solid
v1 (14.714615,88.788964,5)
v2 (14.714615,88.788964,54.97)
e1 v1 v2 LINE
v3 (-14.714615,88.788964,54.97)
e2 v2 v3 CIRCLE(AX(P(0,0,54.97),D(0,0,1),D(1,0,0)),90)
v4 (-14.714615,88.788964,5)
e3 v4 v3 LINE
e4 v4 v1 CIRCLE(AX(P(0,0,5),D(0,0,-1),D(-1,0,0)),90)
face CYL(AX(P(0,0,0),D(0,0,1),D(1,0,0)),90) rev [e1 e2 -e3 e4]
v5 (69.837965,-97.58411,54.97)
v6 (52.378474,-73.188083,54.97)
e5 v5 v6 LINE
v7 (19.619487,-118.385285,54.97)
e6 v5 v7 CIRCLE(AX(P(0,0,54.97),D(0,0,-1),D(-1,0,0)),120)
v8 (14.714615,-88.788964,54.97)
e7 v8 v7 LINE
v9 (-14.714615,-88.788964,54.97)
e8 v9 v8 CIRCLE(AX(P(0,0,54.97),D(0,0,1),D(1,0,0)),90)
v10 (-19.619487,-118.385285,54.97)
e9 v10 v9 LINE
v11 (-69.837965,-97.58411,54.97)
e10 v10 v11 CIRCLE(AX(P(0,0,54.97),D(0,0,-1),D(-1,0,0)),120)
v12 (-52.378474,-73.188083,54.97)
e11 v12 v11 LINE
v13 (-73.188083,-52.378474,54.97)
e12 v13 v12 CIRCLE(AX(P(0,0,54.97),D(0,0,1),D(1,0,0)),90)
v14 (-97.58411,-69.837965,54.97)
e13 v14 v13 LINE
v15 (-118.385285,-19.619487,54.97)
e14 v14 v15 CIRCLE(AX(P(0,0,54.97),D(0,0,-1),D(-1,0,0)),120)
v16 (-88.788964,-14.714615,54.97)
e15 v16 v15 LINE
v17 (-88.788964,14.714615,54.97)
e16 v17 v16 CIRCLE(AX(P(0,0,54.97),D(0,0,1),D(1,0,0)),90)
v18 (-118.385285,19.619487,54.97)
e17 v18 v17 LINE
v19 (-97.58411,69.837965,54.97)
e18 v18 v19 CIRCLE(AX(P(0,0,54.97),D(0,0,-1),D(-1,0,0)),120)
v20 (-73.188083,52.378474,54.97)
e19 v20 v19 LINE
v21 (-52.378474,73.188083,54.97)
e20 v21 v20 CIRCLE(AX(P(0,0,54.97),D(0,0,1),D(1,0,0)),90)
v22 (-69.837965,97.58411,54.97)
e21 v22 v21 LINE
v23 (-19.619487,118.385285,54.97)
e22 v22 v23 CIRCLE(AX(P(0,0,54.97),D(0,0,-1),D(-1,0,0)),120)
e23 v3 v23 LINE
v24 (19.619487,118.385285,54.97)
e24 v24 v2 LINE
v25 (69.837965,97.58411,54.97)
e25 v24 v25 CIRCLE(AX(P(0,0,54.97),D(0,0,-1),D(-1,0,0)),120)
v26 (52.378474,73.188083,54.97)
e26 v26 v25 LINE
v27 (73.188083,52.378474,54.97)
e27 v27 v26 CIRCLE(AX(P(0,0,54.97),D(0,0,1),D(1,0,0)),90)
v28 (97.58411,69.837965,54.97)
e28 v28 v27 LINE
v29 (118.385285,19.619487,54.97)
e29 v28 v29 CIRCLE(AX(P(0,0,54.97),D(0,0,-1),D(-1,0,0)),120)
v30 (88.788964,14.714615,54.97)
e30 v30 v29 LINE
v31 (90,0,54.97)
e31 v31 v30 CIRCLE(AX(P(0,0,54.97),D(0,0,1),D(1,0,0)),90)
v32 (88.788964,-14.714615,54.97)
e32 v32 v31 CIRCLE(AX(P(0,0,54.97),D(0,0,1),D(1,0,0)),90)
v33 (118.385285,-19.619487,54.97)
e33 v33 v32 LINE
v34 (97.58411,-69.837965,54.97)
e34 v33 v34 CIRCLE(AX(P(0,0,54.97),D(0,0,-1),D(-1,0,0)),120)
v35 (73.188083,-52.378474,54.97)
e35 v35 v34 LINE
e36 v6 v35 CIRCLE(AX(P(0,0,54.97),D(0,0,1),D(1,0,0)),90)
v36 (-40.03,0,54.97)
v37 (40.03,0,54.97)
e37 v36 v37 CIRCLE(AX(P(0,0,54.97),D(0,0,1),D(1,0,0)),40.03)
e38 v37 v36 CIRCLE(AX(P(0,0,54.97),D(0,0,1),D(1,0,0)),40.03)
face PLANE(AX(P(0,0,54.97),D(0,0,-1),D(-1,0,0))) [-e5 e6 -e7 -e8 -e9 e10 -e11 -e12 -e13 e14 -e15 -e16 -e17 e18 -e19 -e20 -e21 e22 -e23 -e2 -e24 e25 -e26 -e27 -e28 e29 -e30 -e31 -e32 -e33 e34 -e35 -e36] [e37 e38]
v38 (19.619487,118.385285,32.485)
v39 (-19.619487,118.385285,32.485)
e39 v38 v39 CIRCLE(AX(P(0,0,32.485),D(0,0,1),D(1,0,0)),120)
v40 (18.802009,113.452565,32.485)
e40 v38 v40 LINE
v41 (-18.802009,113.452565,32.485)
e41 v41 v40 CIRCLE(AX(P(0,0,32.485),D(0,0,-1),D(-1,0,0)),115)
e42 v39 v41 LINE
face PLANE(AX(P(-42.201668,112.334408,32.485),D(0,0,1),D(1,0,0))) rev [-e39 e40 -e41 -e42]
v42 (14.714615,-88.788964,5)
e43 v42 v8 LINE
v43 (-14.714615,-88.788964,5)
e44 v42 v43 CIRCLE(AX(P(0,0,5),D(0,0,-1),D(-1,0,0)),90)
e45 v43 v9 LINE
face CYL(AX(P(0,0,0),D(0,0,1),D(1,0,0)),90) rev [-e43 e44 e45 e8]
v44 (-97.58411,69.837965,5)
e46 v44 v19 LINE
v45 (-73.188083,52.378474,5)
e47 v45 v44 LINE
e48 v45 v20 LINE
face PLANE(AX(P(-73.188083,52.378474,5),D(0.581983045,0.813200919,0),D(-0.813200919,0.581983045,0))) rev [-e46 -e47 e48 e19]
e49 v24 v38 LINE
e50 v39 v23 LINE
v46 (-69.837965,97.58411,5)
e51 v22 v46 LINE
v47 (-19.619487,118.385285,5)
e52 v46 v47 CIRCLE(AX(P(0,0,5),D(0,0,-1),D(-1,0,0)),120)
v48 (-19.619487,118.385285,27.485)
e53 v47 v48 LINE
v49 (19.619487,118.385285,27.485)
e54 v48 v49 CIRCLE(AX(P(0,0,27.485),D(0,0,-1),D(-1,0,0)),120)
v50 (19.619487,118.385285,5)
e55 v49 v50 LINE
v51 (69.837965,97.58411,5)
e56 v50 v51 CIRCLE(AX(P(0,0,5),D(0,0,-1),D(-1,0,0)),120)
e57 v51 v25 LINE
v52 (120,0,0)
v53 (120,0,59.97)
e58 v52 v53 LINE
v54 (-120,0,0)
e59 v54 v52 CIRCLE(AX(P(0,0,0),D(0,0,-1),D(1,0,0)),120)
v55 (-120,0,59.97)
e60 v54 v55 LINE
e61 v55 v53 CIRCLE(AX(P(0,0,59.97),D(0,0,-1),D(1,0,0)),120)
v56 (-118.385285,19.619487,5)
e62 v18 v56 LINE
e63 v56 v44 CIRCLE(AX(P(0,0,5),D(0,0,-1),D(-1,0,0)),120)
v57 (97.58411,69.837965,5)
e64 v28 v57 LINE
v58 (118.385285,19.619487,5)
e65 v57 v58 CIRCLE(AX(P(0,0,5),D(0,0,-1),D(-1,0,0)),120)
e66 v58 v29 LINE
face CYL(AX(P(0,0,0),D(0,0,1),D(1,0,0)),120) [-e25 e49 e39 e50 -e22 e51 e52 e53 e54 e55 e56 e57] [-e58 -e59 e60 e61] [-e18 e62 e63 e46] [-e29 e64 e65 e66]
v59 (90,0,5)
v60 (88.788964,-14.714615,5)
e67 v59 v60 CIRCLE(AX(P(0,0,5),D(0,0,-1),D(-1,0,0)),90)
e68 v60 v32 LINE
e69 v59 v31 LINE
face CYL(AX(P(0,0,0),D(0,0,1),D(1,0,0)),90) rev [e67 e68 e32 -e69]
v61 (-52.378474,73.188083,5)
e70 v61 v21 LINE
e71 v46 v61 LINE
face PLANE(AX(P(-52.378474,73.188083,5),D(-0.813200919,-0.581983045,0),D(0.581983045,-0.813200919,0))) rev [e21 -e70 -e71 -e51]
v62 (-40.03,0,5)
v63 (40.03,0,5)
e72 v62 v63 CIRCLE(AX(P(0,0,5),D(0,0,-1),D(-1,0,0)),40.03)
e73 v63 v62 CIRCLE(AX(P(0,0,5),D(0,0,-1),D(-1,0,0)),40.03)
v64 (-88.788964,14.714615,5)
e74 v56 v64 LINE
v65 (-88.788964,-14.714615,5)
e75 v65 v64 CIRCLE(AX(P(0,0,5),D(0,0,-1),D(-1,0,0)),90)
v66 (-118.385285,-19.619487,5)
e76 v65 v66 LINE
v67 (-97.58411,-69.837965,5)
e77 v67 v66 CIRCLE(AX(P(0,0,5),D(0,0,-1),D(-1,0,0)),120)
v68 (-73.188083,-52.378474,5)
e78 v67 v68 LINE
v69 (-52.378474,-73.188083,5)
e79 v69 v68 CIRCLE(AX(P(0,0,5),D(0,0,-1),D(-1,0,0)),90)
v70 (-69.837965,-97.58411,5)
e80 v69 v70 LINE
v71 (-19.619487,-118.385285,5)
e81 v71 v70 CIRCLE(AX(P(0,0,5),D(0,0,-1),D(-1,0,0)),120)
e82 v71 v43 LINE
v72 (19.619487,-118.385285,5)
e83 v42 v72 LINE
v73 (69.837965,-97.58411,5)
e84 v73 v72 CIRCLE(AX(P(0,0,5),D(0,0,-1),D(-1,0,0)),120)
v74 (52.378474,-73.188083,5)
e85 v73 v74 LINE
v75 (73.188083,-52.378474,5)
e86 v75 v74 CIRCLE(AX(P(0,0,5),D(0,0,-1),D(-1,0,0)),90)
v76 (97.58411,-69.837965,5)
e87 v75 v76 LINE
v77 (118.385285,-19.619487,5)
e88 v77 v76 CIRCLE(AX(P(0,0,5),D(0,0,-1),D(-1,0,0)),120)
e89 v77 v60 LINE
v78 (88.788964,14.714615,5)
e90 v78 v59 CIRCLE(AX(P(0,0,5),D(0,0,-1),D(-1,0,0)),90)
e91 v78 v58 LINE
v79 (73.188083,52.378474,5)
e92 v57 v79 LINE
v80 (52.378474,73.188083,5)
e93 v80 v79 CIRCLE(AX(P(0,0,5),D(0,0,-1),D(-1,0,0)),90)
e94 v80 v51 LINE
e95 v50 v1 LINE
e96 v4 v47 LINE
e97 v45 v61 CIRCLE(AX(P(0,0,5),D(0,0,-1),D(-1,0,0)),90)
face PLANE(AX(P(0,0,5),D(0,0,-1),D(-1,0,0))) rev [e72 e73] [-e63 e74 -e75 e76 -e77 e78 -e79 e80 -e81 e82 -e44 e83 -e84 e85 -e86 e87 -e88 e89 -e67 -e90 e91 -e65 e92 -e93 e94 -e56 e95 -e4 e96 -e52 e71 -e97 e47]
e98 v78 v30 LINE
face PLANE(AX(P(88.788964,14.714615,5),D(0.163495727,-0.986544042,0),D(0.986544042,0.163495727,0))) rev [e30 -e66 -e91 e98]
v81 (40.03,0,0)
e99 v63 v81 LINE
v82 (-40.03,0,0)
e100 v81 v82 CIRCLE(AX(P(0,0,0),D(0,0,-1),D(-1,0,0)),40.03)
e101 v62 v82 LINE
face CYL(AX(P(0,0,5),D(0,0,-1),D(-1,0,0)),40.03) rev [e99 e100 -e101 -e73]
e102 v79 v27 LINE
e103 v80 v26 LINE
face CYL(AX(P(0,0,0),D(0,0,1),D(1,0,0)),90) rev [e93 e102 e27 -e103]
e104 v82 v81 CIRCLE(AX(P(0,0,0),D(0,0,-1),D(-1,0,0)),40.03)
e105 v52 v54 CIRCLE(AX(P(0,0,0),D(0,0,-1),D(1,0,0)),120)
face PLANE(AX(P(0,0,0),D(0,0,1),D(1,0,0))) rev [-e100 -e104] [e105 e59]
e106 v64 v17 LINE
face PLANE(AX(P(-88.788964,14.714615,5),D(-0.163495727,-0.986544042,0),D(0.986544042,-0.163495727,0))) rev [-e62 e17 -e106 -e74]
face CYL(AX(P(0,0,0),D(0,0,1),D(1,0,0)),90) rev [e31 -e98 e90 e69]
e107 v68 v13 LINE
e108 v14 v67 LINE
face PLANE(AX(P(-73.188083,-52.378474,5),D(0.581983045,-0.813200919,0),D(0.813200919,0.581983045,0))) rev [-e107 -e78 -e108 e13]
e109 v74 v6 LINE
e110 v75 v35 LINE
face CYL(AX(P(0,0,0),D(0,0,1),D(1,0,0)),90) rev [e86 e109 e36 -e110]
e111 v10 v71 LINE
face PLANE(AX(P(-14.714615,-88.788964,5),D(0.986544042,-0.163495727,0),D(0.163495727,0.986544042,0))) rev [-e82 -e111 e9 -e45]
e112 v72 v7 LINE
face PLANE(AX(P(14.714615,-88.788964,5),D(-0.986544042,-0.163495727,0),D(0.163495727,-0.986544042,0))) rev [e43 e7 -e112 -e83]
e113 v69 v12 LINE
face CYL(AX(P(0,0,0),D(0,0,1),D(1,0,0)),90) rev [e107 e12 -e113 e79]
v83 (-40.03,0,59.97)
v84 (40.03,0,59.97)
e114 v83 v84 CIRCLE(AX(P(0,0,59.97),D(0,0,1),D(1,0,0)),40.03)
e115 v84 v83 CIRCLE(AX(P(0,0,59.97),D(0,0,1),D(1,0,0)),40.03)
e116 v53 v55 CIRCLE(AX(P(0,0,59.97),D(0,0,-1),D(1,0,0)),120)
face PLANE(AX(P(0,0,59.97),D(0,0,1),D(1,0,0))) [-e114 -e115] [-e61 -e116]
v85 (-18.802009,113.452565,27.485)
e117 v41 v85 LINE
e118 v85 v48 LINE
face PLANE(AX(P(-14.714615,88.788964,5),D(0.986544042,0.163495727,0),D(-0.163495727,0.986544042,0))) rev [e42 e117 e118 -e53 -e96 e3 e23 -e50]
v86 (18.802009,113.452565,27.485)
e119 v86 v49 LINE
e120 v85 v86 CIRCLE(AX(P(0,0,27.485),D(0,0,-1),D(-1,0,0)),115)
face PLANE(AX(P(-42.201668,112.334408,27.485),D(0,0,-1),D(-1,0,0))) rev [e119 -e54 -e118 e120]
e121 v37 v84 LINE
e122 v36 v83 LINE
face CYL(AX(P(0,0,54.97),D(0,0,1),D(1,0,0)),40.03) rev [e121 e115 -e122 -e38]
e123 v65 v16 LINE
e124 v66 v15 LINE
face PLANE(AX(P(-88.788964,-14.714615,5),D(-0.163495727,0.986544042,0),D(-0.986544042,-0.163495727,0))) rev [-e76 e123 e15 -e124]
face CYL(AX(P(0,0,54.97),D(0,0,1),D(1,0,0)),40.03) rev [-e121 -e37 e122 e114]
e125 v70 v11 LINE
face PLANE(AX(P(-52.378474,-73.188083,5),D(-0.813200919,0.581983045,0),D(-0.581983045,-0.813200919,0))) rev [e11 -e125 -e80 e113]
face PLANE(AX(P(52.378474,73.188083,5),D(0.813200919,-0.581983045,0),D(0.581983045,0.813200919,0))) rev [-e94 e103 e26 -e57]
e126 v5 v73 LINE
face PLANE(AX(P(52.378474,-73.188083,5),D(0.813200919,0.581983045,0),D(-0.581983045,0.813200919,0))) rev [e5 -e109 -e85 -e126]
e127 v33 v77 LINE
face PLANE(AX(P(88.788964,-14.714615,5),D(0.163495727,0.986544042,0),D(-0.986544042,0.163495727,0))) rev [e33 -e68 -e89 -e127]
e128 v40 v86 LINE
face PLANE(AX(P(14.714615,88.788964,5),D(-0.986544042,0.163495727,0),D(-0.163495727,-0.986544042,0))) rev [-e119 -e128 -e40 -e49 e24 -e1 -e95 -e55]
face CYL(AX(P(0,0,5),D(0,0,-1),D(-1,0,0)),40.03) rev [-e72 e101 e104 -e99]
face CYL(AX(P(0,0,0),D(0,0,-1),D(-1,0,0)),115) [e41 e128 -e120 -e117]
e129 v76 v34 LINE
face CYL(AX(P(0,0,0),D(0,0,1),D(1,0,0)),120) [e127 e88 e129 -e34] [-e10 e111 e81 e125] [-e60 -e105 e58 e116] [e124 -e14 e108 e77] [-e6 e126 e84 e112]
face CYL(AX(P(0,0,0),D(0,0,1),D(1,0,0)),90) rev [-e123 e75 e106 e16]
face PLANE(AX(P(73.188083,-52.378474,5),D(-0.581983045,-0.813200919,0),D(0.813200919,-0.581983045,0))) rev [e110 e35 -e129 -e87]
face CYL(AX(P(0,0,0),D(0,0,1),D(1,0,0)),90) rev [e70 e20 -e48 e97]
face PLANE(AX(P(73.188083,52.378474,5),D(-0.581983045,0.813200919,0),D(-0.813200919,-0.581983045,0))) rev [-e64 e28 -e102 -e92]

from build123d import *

# Parameters (mm, degrees)
SKETCH1_R           = 150
SKETCH1_R_2         = 120
BOSS_EXTRUDE1_DEPTH = 59.97
BOSS_EXTRUDE2_START = -59.97
SKETCH2_R           = 120
SKETCH2_R_2         = 90
BOSS_EXTRUDE2_DEPTH = 59.97
CUT_EXTRUDE1_START  = -59.97
CUT_EXTRUDE1_DEPTH  = 59.97
CIRPATTERN1_COUNT   = 8
CUT_EXTRUDE2_START  = -49.97
CUT_EXTRUDE2_DEPTH  = 49.97
CIRPATTERN2_COUNT   = 8
BOSS_EXTRUDE3_START = -5
SKETCH6_R           = 90
SKETCH6_R_2         = 40.03
BOSS_EXTRUDE3_DEPTH = 5
SKETCH7_R           = 90
SKETCH7_R_2         = 40.03
BOSS_EXTRUDE4_DEPTH = 5
SKETCH8_R           = 150
SKETCH8_R_2         = 120
CUT_EXTRUDE3_DEPTH  = 80
SKETCH10_W          = 5
SKETCH10_H          = 5
CUT_REVOLVE1_ANGLE  = 30


with BuildPart() as part:
    # Sketch1 → Boss-Extrude1 (new body)
    with BuildSketch(Plane.XY):
        Circle(SKETCH1_R)
        Circle(SKETCH1_R_2, mode=Mode.SUBTRACT)
    extrude(amount=BOSS_EXTRUDE1_DEPTH)

    # Sketch2 → Boss-Extrude2 (add)
    with BuildSketch(Plane.XY.offset(59.97).offset(BOSS_EXTRUDE2_START)):
        Circle(SKETCH2_R)
        Circle(SKETCH2_R_2, mode=Mode.SUBTRACT)
    extrude(amount=BOSS_EXTRUDE2_DEPTH)

    # Sketch3 → Cut-Extrude1 (cut)
    with BuildSketch(Plane.XY.offset(59.97).offset(CUT_EXTRUDE1_START)):
        with BuildLine():
            Line((-15.663143066, 118.973383365), (-19.578928833, 148.716729206))
            ThreePointArc((-19.578928833, 148.716729206), (0, 150), (19.578928833, 148.716729206))
            Line((19.578928833, 148.716729206), (15.663143066, 118.973383365))
            ThreePointArc((15.663143066, 118.973383365), (0, 120), (-15.663143066, 118.973383365))
        make_face()
    cut_extrude1 = extrude(amount=CUT_EXTRUDE1_DEPTH, mode=Mode.SUBTRACT)

    # CirPattern1: Cut-Extrude1 ×8 about axis
    cirpattern1_axis = Axis((0, 0, 0), (0, 0, 1))
    for i in range(1, CIRPATTERN1_COUNT):
        add(cut_extrude1.rotate(cirpattern1_axis, i * 360 / CIRPATTERN1_COUNT), mode=Mode.SUBTRACT)

    # Sketch5 → Cut-Extrude2 (cut)
    with BuildSketch(Plane.XY.offset(54.97).offset(CUT_EXTRUDE2_START)):
        with BuildLine():
            Line((14.714615406, 88.788963804), (24.524359011, 147.98160634))
            ThreePointArc((24.524359011, 147.98160634), (57.402514855, 138.581929877), (87.297456773, 121.980137895))
            Line((87.297456773, 121.980137895), (52.378474064, 73.188082737))
            ThreePointArc((52.378474064, 73.188082737), (34.441508913, 83.149157926), (14.714615406, 88.788963804))
        make_face()
    cut_extrude2 = extrude(amount=CUT_EXTRUDE2_DEPTH, mode=Mode.SUBTRACT)

    # CirPattern2: Cut-Extrude2 ×8 about axis
    cirpattern2_axis = Axis((0, 0, 0), (0, 0, 1))
    for i in range(1, CIRPATTERN2_COUNT):
        add(cut_extrude2.rotate(cirpattern2_axis, i * 360 / CIRPATTERN2_COUNT), mode=Mode.SUBTRACT)

    # Sketch6 → Boss-Extrude3 (add)
    with BuildSketch(Plane.XY.offset(59.97).offset(BOSS_EXTRUDE3_START)):
        Circle(SKETCH6_R)
        Circle(SKETCH6_R_2, mode=Mode.SUBTRACT)
    extrude(amount=BOSS_EXTRUDE3_DEPTH)

    # Sketch7 → Boss-Extrude4 (add)
    with BuildSketch(Plane(origin=(0, 0, 0), x_dir=(-1, 0, 0), z_dir=(0, 0, -1))):
        Circle(SKETCH7_R)
        with Locations(Location((0, 0, 0), (0, 0, 180))):
            Circle(SKETCH7_R_2, mode=Mode.SUBTRACT)
    extrude(amount=-BOSS_EXTRUDE4_DEPTH)

    # Sketch8 → Cut-Extrude3 (cut)
    with BuildSketch(Plane(origin=(0, 0, 0), x_dir=(-1, 0, 0), z_dir=(0, 0, -1))):
        Circle(SKETCH8_R)
        with Locations(Location((0, 0, 0), (0, 0, 180))):
            Circle(SKETCH8_R_2, mode=Mode.SUBTRACT)
    extrude(amount=-CUT_EXTRUDE3_DEPTH, mode=Mode.SUBTRACT)

    # Sketch10 → Cut-Revolve1 (revolve, cut)
    with BuildSketch(Plane(origin=(0, 0, 0), x_dir=(0, 0, -1), z_dir=(0.9865440422698816, -0.16349572673865878, 0))):
        with Locations((-29.985, 117.5)):
            Rectangle(SKETCH10_W, SKETCH10_H)
    revolve(axis=Axis((0, 0, 0), (0, 0, 1)), revolution_arc=CUT_REVOLVE1_ANGLE, mode=Mode.SUBTRACT)


solid = part.part
